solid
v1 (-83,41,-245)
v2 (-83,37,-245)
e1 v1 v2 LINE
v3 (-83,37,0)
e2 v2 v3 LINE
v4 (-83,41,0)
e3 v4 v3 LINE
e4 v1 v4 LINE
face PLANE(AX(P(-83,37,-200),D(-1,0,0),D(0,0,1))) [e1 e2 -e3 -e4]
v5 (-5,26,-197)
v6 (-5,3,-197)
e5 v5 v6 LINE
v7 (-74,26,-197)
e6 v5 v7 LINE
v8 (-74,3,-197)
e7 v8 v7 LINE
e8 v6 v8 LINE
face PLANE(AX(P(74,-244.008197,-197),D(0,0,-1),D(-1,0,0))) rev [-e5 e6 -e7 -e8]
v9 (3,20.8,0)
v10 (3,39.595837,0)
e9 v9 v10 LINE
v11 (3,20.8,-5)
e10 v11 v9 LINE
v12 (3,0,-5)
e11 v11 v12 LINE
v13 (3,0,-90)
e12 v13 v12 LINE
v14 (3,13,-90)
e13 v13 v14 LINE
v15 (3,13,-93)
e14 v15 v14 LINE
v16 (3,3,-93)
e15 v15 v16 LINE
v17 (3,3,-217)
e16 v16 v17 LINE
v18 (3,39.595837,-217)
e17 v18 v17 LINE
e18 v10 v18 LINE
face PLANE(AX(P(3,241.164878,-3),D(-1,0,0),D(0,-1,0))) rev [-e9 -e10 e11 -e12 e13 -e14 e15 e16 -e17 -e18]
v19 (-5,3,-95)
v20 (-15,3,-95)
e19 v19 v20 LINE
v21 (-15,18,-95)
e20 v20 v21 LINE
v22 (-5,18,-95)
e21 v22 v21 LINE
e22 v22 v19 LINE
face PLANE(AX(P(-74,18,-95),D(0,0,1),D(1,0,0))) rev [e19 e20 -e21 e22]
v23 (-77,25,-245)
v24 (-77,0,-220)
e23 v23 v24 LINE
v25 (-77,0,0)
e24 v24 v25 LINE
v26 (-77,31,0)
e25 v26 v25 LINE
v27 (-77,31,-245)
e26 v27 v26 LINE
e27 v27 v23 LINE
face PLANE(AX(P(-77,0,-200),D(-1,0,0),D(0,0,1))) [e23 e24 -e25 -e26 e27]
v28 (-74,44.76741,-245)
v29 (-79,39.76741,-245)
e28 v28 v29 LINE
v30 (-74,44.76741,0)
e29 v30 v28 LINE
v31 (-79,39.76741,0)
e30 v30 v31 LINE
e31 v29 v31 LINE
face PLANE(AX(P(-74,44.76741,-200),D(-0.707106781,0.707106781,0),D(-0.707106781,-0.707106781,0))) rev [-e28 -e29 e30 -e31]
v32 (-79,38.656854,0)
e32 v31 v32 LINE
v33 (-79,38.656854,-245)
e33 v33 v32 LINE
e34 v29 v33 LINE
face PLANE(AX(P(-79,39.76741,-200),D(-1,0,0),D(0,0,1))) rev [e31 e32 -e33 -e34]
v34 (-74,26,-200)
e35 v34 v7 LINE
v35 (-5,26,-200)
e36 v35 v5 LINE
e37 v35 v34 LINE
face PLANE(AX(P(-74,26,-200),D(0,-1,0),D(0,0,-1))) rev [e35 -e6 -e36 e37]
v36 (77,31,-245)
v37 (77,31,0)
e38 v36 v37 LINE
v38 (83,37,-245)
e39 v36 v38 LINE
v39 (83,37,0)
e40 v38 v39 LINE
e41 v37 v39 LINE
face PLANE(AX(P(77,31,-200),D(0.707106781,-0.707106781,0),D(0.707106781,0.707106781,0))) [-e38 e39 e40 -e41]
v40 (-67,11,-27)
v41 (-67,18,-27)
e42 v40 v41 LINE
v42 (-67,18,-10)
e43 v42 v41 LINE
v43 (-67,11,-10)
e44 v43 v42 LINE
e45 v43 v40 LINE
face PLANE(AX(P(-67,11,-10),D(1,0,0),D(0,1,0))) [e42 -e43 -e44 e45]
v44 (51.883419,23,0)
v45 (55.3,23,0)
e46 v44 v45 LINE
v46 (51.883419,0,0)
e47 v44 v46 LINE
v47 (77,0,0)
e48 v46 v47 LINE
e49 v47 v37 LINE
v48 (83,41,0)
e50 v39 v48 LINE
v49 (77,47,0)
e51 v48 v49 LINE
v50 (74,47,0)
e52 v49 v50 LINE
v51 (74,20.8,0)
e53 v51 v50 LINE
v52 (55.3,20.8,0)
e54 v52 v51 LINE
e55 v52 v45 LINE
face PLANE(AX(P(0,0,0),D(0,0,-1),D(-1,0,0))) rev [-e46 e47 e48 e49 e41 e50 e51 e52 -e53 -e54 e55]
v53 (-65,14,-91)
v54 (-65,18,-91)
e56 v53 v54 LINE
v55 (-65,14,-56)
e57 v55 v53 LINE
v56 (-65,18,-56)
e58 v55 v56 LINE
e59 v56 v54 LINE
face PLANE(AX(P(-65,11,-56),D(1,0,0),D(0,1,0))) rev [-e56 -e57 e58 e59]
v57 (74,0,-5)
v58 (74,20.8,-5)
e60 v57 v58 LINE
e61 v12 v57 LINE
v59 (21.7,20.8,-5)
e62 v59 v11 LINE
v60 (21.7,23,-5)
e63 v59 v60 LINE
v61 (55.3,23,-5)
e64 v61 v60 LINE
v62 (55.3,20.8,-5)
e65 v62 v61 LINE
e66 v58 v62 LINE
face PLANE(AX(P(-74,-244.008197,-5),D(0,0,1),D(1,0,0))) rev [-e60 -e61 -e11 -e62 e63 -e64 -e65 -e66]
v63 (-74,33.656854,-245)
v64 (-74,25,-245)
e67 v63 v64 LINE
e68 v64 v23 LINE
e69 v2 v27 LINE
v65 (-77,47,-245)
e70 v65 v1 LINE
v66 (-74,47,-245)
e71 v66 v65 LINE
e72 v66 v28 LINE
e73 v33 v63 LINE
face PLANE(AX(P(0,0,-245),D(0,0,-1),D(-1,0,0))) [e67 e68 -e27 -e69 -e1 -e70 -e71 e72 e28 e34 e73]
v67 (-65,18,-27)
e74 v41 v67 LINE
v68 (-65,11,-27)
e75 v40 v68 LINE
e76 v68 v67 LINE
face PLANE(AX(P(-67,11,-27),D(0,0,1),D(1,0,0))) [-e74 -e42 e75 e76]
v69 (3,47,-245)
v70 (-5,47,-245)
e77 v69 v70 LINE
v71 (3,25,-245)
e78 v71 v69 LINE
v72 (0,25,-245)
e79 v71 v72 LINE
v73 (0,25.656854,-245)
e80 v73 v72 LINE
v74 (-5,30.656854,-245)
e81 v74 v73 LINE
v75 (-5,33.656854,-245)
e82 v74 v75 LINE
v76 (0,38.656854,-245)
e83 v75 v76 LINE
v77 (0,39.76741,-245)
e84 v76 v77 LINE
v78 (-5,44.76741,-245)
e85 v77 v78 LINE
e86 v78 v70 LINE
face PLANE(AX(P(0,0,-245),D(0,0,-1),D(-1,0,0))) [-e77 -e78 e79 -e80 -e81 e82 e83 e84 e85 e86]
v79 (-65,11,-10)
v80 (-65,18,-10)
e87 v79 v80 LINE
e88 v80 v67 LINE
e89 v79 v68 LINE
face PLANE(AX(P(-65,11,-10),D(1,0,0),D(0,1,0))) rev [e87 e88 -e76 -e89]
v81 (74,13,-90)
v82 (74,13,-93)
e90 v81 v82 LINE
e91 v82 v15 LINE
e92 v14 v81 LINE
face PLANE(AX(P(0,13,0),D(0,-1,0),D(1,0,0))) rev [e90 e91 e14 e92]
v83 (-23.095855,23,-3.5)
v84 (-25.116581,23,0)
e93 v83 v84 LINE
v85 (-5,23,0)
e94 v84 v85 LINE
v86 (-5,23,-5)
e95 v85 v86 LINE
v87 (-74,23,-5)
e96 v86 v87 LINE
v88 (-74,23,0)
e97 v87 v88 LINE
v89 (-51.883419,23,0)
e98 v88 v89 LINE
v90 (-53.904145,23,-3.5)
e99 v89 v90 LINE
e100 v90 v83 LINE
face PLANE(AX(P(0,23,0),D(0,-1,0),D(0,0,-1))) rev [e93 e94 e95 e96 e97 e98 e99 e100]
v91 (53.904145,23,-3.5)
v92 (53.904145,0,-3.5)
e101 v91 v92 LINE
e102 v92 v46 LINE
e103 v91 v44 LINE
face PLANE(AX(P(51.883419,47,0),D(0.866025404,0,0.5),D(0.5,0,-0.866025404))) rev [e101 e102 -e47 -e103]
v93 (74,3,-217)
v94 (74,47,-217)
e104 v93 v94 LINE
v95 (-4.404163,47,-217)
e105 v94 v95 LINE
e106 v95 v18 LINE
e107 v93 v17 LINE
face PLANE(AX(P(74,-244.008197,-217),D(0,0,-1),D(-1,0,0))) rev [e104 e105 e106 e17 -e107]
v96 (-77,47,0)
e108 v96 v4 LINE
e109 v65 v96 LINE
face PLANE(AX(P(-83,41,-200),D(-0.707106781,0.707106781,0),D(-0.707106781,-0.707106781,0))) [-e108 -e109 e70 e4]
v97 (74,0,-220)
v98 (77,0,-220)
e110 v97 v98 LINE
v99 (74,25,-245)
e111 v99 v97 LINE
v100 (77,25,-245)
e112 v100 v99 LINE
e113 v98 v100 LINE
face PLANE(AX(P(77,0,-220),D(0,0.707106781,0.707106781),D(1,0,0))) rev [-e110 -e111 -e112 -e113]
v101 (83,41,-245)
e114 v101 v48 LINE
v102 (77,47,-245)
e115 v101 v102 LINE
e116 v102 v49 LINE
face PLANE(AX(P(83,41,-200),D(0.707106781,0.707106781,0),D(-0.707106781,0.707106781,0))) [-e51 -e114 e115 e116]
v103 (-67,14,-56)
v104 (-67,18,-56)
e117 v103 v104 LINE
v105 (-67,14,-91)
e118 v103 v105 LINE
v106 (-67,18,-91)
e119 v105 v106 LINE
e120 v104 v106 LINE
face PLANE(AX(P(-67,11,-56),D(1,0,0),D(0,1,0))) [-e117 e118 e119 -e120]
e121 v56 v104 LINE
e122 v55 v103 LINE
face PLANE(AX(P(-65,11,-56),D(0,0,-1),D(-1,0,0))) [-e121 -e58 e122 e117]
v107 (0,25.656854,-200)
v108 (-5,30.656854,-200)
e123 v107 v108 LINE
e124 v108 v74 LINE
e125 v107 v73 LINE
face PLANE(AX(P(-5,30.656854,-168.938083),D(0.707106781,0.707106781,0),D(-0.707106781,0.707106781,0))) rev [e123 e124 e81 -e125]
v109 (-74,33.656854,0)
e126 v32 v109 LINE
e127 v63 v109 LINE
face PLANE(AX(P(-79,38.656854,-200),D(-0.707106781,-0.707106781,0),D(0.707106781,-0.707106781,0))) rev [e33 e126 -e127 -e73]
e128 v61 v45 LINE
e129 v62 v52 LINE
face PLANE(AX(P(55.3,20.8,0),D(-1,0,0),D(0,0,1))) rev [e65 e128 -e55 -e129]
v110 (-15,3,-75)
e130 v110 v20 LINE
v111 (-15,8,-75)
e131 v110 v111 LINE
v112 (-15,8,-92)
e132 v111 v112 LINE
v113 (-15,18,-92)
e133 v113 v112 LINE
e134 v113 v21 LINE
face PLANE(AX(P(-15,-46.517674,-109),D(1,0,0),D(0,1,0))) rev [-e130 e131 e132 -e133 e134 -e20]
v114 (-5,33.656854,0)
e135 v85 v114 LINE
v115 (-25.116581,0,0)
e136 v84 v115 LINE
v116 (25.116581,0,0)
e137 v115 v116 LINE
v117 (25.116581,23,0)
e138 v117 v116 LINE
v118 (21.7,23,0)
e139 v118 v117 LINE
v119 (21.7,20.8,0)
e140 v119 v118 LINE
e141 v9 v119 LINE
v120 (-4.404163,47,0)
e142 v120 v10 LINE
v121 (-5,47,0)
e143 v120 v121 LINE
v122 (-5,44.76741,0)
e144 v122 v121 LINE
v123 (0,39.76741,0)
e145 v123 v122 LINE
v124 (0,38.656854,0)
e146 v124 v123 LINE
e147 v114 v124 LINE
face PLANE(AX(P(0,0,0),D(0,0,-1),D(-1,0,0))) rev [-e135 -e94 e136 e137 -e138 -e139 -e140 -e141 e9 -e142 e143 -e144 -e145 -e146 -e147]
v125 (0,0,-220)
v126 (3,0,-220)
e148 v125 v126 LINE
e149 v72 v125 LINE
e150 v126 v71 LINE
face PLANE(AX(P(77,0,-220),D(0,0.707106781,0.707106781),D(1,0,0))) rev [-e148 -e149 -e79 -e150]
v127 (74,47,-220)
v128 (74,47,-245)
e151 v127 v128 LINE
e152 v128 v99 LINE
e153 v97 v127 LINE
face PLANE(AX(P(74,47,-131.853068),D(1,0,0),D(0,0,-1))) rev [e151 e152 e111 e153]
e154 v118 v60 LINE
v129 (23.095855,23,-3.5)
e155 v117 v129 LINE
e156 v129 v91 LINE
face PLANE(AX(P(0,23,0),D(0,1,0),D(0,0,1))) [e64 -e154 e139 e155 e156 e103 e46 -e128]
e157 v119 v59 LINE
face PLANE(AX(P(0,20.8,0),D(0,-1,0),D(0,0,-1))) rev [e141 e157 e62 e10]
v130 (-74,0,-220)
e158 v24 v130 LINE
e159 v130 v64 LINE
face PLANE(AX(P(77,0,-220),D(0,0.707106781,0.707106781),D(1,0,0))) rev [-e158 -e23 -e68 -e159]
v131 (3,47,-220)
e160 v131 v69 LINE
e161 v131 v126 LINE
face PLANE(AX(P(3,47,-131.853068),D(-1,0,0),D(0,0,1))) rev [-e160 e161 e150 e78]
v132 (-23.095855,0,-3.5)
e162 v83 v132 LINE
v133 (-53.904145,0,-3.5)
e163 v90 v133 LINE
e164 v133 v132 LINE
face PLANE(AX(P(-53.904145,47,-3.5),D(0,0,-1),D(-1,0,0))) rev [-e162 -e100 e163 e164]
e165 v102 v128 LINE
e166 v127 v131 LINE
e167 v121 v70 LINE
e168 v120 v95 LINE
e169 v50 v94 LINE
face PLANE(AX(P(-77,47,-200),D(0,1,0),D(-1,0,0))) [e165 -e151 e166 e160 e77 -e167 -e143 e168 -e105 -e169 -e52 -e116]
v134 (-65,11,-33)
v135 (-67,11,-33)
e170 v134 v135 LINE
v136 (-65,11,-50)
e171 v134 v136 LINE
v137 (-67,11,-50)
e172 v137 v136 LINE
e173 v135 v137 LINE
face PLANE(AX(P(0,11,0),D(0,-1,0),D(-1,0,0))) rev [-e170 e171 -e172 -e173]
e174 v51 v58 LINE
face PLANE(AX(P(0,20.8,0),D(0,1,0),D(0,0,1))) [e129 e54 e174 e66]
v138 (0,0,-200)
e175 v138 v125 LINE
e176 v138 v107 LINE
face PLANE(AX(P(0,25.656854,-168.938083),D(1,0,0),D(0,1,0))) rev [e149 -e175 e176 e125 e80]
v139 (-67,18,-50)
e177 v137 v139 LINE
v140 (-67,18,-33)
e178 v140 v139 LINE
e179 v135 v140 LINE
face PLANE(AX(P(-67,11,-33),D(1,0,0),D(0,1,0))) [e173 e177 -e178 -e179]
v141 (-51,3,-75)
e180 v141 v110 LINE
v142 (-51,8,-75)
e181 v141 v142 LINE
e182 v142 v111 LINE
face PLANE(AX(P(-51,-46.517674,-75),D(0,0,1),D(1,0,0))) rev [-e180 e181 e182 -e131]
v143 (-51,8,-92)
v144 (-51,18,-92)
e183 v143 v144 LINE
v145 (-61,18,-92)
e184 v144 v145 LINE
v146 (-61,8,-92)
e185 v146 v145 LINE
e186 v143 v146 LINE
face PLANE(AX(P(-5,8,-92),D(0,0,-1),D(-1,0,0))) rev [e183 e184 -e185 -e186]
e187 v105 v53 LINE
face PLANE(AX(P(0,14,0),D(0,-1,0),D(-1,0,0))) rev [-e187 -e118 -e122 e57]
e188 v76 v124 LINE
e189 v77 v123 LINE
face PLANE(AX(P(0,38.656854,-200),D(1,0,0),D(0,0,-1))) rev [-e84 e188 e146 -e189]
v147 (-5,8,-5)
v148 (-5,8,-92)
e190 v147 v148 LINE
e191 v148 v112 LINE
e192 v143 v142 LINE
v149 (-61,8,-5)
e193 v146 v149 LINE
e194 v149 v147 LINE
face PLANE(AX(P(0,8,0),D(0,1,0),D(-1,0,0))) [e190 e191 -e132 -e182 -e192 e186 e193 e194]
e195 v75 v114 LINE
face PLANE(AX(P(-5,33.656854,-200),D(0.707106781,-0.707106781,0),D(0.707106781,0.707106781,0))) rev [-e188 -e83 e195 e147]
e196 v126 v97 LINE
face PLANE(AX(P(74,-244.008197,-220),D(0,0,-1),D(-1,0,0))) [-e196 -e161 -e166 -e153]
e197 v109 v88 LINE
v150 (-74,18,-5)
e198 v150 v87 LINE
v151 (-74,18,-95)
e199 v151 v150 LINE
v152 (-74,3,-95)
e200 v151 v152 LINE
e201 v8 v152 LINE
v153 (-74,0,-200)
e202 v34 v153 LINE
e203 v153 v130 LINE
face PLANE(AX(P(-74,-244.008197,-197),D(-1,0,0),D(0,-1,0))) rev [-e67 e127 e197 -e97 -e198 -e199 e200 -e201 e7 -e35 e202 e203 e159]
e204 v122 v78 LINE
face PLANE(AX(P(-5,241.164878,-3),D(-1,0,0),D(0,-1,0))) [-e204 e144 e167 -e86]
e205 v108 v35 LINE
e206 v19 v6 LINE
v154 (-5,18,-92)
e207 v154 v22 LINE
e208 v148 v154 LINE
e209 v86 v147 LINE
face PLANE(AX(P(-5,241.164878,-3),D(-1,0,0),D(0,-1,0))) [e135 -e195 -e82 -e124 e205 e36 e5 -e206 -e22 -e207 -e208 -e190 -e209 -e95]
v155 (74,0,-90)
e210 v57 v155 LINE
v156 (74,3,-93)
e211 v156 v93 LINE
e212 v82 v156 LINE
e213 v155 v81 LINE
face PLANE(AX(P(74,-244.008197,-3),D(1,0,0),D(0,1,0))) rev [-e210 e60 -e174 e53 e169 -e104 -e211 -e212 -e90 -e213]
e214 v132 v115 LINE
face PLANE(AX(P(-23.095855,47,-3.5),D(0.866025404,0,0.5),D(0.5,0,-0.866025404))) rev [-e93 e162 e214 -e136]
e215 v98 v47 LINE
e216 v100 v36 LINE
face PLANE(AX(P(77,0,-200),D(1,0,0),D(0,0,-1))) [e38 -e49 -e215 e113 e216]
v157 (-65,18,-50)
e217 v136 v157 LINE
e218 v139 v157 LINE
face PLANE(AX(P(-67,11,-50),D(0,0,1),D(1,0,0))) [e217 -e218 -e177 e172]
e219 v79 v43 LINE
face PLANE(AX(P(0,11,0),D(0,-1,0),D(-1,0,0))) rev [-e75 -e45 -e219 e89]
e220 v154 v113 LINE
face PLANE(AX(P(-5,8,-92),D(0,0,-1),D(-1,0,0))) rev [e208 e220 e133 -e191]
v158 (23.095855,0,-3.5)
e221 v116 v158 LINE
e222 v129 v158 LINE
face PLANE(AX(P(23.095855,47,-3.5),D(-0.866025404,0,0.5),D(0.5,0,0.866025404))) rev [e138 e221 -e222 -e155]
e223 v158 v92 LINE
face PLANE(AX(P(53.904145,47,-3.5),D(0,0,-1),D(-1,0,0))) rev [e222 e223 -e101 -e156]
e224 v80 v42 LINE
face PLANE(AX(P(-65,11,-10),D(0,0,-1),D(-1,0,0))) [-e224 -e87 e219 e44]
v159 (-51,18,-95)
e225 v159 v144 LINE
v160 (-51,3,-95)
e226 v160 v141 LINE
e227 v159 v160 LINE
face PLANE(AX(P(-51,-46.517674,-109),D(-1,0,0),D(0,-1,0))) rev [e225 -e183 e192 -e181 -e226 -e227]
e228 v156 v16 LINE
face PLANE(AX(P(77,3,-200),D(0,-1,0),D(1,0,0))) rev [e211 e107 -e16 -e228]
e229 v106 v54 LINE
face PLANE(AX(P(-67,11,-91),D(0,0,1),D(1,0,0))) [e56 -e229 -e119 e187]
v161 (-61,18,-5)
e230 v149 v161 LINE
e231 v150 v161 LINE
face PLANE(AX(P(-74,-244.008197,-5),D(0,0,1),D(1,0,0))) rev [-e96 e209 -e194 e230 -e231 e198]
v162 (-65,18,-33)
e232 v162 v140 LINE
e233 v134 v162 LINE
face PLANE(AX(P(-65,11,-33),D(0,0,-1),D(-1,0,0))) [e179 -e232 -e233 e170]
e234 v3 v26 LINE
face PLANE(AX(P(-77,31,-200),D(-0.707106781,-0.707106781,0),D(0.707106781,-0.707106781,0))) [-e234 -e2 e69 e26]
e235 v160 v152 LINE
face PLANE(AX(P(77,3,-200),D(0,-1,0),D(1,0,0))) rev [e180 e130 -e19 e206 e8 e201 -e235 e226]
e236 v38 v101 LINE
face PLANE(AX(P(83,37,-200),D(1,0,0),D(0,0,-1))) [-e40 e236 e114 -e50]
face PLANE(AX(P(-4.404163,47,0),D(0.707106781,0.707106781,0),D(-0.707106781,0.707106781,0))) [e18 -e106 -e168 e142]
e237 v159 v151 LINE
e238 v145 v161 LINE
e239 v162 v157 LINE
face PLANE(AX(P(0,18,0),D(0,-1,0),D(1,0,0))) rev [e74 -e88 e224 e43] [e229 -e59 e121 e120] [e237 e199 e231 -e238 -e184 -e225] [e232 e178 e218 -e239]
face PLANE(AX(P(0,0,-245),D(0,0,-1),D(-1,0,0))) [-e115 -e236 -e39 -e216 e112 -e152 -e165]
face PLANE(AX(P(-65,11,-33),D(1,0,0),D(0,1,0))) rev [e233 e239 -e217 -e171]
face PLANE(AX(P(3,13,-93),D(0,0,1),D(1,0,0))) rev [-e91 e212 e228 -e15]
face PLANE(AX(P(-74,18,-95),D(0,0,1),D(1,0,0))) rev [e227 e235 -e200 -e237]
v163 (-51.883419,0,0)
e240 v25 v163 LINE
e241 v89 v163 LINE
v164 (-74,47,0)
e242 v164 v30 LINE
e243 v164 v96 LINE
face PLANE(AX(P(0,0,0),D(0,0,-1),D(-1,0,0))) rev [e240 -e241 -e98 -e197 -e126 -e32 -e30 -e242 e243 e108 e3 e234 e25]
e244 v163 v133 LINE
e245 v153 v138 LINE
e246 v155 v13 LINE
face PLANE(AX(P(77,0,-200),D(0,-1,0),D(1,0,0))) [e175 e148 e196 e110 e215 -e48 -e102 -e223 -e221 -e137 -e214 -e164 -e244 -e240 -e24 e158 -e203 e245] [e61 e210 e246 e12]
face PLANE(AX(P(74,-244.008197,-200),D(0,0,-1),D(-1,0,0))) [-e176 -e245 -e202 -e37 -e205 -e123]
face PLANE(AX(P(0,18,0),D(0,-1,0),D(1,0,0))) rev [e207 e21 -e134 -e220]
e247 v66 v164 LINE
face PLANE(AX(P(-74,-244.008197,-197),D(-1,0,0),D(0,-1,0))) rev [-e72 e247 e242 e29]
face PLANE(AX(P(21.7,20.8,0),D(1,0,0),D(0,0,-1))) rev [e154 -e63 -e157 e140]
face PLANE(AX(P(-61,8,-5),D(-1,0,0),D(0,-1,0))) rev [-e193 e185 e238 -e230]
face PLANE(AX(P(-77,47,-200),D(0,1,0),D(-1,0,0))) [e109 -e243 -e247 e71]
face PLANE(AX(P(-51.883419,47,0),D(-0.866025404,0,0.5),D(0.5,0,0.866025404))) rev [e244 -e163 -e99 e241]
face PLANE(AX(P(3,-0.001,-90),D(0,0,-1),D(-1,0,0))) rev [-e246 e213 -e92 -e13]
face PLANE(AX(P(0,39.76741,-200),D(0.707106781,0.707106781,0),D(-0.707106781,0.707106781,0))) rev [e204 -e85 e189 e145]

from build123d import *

# Parameters (mm, degrees)
BOSS_EXTRUDE1_DEPTH     = 200
SKETCH2_W               = 148
SKETCH2_H               = 194
CUT_EXTRUDE1_DEPTH      = 44
SKETCH4_W               = 8
SKETCH4_H               = 194
EXTRUDE_THIN1_DEPTH     = 44
CUT_EXTRUDE2_DEPTH      = 222.580685079
CUT_EXTRUDE3_DEPTH      = 219.876677606
MOVE_FACE1_BY           = 2
MOVE_FACE1_2_BY         = 2
CUT_EXTRUDE4_DEPTH      = 222.580685079
CUT_EXTRUDE5_DEPTH      = 16.595837
MOVE_FACE2_BY           = 45
MOVE_FACE3_BY           = 20
SKETCH9_W               = 71
SKETCH9_H               = 47
CUT_EXTRUDE6_DEPTH      = 25
SKETCH10_W              = 69
SKETCH10_H              = 26
CUT_EXTRUDE7_DEPTH      = 45
CUT_EXTRUDE8_DEPTH      = 45
CHAMFER1_SIZE           = 25
CUT_EXTRUDE9_REACH      = 264.393
SKETCH12_W              = 71
SKETCH12_H              = 85
SKETCH13_W              = 71
SKETCH13_H              = 3
BOSS_EXTRUDE2_DEPTH     = 10
SKETCH14_W              = 18.7
SKETCH14_H              = 5
CUT_EXTRUDE10_DEPTH     = 2.2
SKETCH15_W              = 69
SKETCH15_H              = 90
BOSS_EXTRUDE3_DEPTH     = 15
SKETCH16_W              = 56
SKETCH16_H              = 87
CUT_EXTRUDE11_DEPTH     = 10
CUT_EXTRUDE12_REACH     = 262.298
SKETCH17_W              = 36
SKETCH17_H              = 34
SKETCH18_W              = 2
SKETCH18_H              = 17
SKETCH18_H_2            = 35
CUT_EXTRUDE_THIN1_DEPTH = 7
MOVE_FACE4_BY           = 3


with BuildPart() as part:
    # Sketch1 → Boss-Extrude1 (new body)
    with BuildSketch(Plane.XY):
        Polygon((77, 0), (-77, 0), (-77, 31), (-83, 37), (-83, 41), (-77, 47), (77, 47), (83, 41), (83, 37), (77, 31), align=None)
    extrude(amount=-BOSS_EXTRUDE1_DEPTH)

    # Sketch2 → Cut-Extrude1 (cut)
    with BuildSketch(Plane(origin=(0, 47, 0), x_dir=(1, 0, 0), z_dir=(0, 1, 0))):
        with Locations((0, 100)):
            Rectangle(SKETCH2_W, SKETCH2_H)
    extrude(amount=-CUT_EXTRUDE1_DEPTH, mode=Mode.SUBTRACT)

    # Sketch4 → Extrude-Thin1 (add)
    with BuildSketch(Plane(origin=(0, 3, 0), x_dir=(1, 0, 0), z_dir=(0, 1, 0))):
        with Locations((-1, 100)):
            Rectangle(SKETCH4_W, SKETCH4_H)
    extrude(amount=EXTRUDE_THIN1_DEPTH)

    # Sketch5 → Cut-Extrude2 (cut, through all)
    with BuildSketch(Plane.XY):
        Polygon((-74, 47), (-74, 44.767409819), (-79, 39.767409819), (-79, 38.656854249), (-74, 33.656854249), (-74, 26), (-5, 26), (-5, 33.656854249), (0, 38.656854249), (0, 39.767409819), (-5, 44.767409819), (-5, 47), align=None)
    extrude(amount=-CUT_EXTRUDE2_DEPTH, mode=Mode.SUBTRACT)

    # Sketch6 → Cut-Extrude3 (cut, through all)
    with BuildSketch(Plane.XY.offset(-197)):
        Polygon((-4.404163056, 47), (3, 39.595836944), (74, 39.595836944), (74, 47), (3, 47), align=None)
    extrude(amount=CUT_EXTRUDE3_DEPTH, mode=Mode.SUBTRACT)

    # Move Face1: a face moved outward by 2.0
    extrude(part.faces().sort_by_distance((-39.5, 14.5, -3))[0], amount=MOVE_FACE1_BY, dir=(0, 0, -1))

    # Move Face1 2: a face moved outward by 2.0
    extrude(part.faces().sort_by_distance((38.5, 21.297918472, -3))[0], amount=MOVE_FACE1_2_BY, dir=(0, 0, -1))

    # Sketch7 → Cut-Extrude4 (cut, through all)
    with BuildSketch(Plane.XZ):
        Polygon((-51.883419246, 0), (-53.904145188, -3.5), (-23.095854812, -3.5), (-25.116580754, 0), align=None)
        Polygon((25.116580754, 0), (51.883419246, 0), (53.904145188, -3.5), (23.095854812, -3.5), align=None)
    extrude(amount=-CUT_EXTRUDE4_DEPTH, mode=Mode.SUBTRACT)

    # Sketch8 → Cut-Extrude5 (cut)
    with BuildSketch(Plane(origin=(0, 39.595836944, 0), x_dir=(1, 0, 0), z_dir=(0, 1, 0))):
        Polygon((25.116580754, 0), (23.095854812, 3.5), (53.904145188, 3.5), (51.883419246, 0), (74, 0), (74, 5), (3, 5), (3, 0), align=None)
        Polygon((-53.904145188, 3.5), (-23.095854812, 3.5), (-25.116580754, 0), (-5, 0), (-5, 5), (-74, 5), (-74, 0), (-51.883419246, 0), align=None)
    extrude(amount=-CUT_EXTRUDE5_DEPTH, mode=Mode.SUBTRACT)

    # Move Face2: a face moved outward by 45.0
    extrude(part.faces().sort_by_distance((10.200110487, 20.43272532, -200))[0], amount=MOVE_FACE2_BY, dir=(0, 0, -1))

    # Move Face3: a face moved inward by 20.0
    extrude(part.faces().sort_by_distance((38.169755743, 25.169887896, -197))[0], amount=MOVE_FACE3_BY, dir=(0, 0, -1), mode=Mode.SUBTRACT)

    # Sketch9 → Cut-Extrude6 (cut)
    with BuildSketch(Plane(origin=(0, 0, -245), x_dir=(-1, 0, 0), z_dir=(0, 0, -1))):
        with Locations((-38.5, 23.5)):
            Rectangle(SKETCH9_W, SKETCH9_H)
    extrude(amount=-CUT_EXTRUDE6_DEPTH, mode=Mode.SUBTRACT)

    # Sketch10 → Cut-Extrude7 (cut)
    with BuildSketch(Plane(origin=(0, 0, -245), x_dir=(-1, 0, 0), z_dir=(0, 0, -1))):
        with Locations((39.5, 13)):
            Rectangle(SKETCH10_W, SKETCH10_H)
    extrude(amount=-CUT_EXTRUDE7_DEPTH, mode=Mode.SUBTRACT)

    # Sketch11 → Cut-Extrude8 (cut)
    with BuildSketch(Plane(origin=(0, 0, -245), x_dir=(-1, 0, 0), z_dir=(0, 0, -1))):
        Polygon((5, 0), (5, 30.656854249), (0, 25.656854249), (0, 0), align=None)
    extrude(amount=-CUT_EXTRUDE8_DEPTH, mode=Mode.SUBTRACT)

    # Chamfer1
    chamfer1_edges = [part.edges().sort_by_distance(p)[0] for p in [
        (-75.5, 0, -245),
        (1.5, 0, -245),
        (75.5, 0, -245),
    ]]
    chamfer(chamfer1_edges, length=CHAMFER1_SIZE)

    # Sketch12 → Cut-Extrude9 (cut, up to next)
    with BuildSketch(Plane(origin=(0, 3, 0), x_dir=(1, 0, 0), z_dir=(0, 1, 0)), mode=Mode.PRIVATE) as cut_extrude9_sk1:
        with Locations((38.5, 47.5)):
            Rectangle(SKETCH12_W, SKETCH12_H)
    cut_extrude9_tool1 = extrude(cut_extrude9_sk1.sketch, amount=-CUT_EXTRUDE9_REACH, mode=Mode.PRIVATE) & part.part
    add(cut_extrude9_tool1.solids().sort_by_distance((38.5, 3, -47.5))[0], mode=Mode.SUBTRACT)

    # Sketch13 → Boss-Extrude2 (add)
    with BuildSketch(Plane(origin=(0, 3, 0), x_dir=(1, 0, 0), z_dir=(0, 1, 0))):
        with Locations((38.5, 91.5)):
            Rectangle(SKETCH13_W, SKETCH13_H)
    extrude(amount=BOSS_EXTRUDE2_DEPTH)

    # Sketch14 → Cut-Extrude10 (cut)
    with BuildSketch(Plane(origin=(0, 23, 0), x_dir=(1, 0, 0), z_dir=(0, 1, 0))):
        with Locations((12.35, 2.5)):
            Rectangle(SKETCH14_W, SKETCH14_H)
        with Locations((64.65, 2.5)):
            Rectangle(SKETCH14_W, SKETCH14_H)
    extrude(amount=-CUT_EXTRUDE10_DEPTH, mode=Mode.SUBTRACT)

    # Sketch15 → Boss-Extrude3 (add)
    with BuildSketch(Plane(origin=(0, 3, 0), x_dir=(1, 0, 0), z_dir=(0, 1, 0))):
        with Locations((-39.5, 50)):
            Rectangle(SKETCH15_W, SKETCH15_H)
    extrude(amount=BOSS_EXTRUDE3_DEPTH)

    # Sketch16 → Cut-Extrude11 (cut)
    with BuildSketch(Plane(origin=(0, 18, 0), x_dir=(1, 0, 0), z_dir=(0, 1, 0))):
        with Locations((-33, 48.5)):
            Rectangle(SKETCH16_W, SKETCH16_H)
    extrude(amount=-CUT_EXTRUDE11_DEPTH, mode=Mode.SUBTRACT)

    # Cut-Extrude12: up to this face of the body (flat: up to its plane)
    cut_extrude12_end = Plane(part.part.faces().sort_by_distance((-39.5, 3, -146))[0])
    # Sketch17 → Cut-Extrude12 (cut, up to the picked face)
    with BuildSketch(Plane(origin=(0, 18, 0), x_dir=(1, 0, 0), z_dir=(0, 1, 0)), mode=Mode.PRIVATE) as cut_extrude12_sk1:
        with Locations((-33, 92)):
            Rectangle(SKETCH17_W, SKETCH17_H)
    cut_extrude12_tool1 = split(extrude(cut_extrude12_sk1.sketch, amount=-CUT_EXTRUDE12_REACH, mode=Mode.PRIVATE), bisect_by=cut_extrude12_end, keep=Keep.BOTH, mode=Mode.PRIVATE)
    add(cut_extrude12_tool1.solids().sort_by(Axis((-33, 18, -92), (0, -1, 0)))[0], mode=Mode.SUBTRACT)

    # Sketch18 → Cut-Extrude-Thin1 (cut)
    with BuildSketch(Plane(origin=(0, 18, 0), x_dir=(1, 0, 0), z_dir=(0, 1, 0))):
        with Locations((-66, 18.5)):
            Rectangle(SKETCH18_W, SKETCH18_H)
        with Locations((-66, 41.5)):
            Rectangle(SKETCH18_W, SKETCH18_H)
        with Locations((-66, 73.5)):
            Rectangle(SKETCH18_W, SKETCH18_H_2)
    extrude(amount=-CUT_EXTRUDE_THIN1_DEPTH, mode=Mode.SUBTRACT)

    # Move Face4: a face moved outward by 3.0
    extrude(part.faces().sort_by_distance((-66, 11, -73.5))[0], amount=MOVE_FACE4_BY, dir=(0, 1, 0))


solid = part.part
